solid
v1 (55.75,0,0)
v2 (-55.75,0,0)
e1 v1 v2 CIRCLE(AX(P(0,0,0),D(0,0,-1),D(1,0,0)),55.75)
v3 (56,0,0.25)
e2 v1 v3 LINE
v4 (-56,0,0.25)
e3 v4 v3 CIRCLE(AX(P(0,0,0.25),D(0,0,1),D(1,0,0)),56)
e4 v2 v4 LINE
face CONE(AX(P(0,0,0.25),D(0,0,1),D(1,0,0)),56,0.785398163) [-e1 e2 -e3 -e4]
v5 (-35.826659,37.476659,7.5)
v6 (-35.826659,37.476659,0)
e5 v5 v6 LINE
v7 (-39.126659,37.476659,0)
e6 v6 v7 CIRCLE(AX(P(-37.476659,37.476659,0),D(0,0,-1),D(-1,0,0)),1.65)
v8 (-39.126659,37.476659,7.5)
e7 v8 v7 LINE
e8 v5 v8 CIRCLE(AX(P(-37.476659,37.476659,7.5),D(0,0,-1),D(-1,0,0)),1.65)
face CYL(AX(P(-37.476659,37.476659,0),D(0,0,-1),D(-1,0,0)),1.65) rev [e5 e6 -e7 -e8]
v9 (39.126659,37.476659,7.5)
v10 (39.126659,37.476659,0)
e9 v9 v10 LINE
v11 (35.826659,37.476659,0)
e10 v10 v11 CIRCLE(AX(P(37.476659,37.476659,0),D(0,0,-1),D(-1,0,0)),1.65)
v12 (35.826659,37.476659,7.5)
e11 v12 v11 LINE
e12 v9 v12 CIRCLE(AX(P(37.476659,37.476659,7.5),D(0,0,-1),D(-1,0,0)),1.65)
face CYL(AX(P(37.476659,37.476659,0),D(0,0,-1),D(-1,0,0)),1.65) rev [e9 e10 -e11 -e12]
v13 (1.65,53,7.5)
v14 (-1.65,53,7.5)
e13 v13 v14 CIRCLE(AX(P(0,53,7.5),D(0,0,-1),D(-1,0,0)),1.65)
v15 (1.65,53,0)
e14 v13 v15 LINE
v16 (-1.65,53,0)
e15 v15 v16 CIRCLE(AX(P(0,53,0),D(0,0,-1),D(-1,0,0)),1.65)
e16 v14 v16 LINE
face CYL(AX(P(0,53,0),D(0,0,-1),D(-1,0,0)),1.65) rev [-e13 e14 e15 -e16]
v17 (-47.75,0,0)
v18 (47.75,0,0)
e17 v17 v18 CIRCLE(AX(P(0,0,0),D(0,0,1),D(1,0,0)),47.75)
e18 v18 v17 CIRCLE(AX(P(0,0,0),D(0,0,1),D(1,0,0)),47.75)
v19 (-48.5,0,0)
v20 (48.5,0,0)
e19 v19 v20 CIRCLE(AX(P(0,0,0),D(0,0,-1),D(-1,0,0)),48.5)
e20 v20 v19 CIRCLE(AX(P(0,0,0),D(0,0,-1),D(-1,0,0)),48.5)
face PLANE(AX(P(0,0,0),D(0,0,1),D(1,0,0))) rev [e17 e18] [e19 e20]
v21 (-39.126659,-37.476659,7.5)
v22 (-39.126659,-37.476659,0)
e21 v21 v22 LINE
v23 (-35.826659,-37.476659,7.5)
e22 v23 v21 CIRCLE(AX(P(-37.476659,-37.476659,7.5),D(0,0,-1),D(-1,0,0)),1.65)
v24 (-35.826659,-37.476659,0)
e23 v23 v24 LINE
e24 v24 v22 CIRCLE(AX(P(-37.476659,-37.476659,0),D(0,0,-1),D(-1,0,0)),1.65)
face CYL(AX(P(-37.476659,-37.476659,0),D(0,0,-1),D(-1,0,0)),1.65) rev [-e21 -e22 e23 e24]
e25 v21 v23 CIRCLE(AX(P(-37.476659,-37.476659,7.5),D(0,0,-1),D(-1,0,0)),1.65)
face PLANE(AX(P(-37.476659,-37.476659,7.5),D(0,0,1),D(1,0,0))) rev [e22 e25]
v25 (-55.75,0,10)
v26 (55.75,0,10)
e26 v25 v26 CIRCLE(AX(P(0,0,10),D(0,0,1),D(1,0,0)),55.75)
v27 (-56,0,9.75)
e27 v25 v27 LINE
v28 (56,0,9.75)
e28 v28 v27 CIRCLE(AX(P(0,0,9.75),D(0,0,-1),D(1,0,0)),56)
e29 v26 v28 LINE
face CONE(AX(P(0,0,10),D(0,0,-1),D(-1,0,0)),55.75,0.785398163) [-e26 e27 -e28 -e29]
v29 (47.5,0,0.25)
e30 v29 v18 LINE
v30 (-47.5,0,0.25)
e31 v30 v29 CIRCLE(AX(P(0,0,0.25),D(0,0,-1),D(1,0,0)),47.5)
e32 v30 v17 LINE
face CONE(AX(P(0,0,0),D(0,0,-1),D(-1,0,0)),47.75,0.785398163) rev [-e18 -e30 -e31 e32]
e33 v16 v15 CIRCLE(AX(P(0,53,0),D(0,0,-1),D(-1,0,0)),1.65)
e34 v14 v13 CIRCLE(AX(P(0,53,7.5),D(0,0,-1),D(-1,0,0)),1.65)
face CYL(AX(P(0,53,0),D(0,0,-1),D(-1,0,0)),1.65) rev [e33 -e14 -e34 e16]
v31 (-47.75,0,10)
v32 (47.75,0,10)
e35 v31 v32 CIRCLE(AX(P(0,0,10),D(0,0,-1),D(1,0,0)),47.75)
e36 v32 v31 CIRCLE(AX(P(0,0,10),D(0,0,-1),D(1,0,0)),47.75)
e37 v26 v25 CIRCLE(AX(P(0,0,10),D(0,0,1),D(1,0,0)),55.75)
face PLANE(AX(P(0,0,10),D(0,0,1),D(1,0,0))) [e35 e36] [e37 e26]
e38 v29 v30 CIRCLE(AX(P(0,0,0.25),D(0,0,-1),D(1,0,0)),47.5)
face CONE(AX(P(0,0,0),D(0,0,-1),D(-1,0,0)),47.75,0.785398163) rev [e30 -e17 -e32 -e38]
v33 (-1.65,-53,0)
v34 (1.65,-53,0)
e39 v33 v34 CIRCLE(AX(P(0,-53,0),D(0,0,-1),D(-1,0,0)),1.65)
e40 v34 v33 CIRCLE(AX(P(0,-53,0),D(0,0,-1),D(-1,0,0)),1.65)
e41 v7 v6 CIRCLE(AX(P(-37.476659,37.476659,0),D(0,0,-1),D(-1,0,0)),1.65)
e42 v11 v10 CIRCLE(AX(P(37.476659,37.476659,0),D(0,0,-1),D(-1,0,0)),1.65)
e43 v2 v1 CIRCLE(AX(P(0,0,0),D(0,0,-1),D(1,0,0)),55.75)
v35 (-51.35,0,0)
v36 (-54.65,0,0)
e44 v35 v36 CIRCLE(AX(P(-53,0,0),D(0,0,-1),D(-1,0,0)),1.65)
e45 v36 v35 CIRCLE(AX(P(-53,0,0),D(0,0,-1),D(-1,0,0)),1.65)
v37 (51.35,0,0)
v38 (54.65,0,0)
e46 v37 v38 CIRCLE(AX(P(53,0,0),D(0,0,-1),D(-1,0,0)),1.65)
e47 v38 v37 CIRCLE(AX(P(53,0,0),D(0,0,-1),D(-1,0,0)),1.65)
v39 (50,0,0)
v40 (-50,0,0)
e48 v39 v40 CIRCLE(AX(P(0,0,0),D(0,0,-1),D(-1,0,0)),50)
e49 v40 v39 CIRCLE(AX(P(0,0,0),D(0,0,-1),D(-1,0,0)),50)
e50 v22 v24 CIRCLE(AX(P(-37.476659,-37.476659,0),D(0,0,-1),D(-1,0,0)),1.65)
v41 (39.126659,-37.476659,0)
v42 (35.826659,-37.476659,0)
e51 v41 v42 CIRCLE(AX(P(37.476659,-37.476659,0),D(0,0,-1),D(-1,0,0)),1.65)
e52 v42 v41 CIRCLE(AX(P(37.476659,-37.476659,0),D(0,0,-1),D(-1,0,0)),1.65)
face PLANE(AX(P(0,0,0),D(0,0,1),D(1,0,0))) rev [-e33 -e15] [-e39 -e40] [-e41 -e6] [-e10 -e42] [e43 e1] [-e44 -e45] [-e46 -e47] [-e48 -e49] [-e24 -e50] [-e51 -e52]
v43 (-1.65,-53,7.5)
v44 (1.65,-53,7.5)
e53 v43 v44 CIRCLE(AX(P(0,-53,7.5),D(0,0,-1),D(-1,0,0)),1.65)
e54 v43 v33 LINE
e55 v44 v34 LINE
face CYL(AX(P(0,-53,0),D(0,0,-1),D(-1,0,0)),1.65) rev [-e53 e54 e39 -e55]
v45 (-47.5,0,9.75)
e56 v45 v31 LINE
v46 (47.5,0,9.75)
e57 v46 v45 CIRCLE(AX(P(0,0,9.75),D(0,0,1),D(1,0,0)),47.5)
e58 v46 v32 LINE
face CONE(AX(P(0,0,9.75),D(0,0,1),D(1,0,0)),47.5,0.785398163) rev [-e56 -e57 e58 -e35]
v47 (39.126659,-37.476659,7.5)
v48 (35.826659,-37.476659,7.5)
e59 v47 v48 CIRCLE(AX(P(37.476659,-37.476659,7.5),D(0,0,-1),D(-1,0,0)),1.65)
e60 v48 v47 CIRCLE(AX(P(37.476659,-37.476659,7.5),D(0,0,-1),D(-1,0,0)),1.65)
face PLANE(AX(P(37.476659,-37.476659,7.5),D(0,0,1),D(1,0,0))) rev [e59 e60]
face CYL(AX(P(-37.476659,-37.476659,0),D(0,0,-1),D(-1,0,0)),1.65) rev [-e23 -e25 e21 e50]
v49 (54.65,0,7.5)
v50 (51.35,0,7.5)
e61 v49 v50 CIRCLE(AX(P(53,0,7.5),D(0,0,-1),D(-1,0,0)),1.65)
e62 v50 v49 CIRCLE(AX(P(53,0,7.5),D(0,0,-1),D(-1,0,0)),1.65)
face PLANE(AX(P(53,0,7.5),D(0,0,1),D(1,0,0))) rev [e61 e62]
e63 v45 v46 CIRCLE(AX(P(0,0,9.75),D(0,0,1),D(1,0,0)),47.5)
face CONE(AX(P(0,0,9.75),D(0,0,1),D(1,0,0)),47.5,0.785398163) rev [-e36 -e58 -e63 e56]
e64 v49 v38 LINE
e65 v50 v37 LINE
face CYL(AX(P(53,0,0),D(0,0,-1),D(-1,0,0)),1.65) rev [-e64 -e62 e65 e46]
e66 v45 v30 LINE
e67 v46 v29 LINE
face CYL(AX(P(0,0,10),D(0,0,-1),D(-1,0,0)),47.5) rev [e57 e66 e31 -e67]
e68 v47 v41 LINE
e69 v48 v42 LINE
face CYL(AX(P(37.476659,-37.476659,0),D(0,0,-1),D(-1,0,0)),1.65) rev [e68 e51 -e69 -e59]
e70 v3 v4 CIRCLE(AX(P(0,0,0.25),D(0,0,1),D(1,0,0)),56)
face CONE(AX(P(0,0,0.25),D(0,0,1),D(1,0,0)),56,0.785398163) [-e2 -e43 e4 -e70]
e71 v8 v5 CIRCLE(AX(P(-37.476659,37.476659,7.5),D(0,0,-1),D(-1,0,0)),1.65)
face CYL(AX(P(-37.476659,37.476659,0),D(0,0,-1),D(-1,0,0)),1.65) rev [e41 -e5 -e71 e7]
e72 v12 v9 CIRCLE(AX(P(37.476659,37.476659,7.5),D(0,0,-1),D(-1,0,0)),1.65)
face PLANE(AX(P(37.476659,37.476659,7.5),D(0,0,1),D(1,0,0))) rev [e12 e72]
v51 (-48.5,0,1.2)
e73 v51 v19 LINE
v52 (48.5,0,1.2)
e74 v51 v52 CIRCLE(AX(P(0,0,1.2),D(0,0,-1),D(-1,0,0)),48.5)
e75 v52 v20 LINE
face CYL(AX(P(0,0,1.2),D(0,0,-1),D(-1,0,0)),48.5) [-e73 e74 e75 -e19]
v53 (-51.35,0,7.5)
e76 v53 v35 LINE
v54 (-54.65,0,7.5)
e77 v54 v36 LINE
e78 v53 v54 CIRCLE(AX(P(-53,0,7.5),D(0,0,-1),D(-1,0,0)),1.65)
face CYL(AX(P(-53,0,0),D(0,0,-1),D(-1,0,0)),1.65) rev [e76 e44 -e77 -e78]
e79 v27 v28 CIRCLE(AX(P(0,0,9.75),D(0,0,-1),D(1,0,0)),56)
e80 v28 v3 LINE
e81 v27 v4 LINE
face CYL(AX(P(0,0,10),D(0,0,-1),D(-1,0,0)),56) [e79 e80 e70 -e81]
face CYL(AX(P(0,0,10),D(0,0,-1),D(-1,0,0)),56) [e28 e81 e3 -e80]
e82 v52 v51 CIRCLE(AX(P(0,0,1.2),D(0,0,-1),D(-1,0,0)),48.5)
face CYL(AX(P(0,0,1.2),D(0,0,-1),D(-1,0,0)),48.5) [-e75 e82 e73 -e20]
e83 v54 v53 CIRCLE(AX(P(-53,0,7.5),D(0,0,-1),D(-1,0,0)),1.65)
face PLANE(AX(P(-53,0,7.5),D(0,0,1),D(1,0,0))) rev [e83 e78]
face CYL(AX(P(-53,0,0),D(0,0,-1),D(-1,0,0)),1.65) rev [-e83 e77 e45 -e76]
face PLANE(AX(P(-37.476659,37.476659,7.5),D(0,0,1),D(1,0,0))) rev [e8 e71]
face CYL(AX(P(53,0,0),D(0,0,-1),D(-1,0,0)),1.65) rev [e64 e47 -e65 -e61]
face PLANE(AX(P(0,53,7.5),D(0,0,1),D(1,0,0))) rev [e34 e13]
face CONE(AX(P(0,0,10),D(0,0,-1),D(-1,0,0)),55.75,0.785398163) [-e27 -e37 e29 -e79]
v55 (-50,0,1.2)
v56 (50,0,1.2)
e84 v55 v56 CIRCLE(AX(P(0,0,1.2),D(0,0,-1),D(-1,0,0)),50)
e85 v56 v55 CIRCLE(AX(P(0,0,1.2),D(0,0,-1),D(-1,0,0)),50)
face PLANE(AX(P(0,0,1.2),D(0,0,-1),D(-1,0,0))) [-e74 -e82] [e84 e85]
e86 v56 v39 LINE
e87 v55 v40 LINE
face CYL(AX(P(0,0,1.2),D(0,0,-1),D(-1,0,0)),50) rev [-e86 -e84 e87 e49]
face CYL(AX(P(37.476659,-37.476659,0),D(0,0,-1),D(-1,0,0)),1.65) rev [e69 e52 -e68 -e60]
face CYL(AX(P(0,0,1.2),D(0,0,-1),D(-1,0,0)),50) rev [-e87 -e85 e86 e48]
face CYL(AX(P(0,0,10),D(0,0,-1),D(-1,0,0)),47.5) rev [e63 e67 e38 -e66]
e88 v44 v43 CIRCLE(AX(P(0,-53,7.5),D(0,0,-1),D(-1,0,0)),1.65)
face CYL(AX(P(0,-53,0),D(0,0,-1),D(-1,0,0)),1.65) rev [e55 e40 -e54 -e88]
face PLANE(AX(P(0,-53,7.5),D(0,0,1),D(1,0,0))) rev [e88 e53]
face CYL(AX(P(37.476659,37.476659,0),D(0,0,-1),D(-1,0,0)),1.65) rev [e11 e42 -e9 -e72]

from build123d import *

# Parameters (mm, degrees)
SKETCH_1_R             = 56
SKETCH_1_R_2           = 47.5
EXTRUDE_1_DEPTH        = 10
HOLE_WIZARD_M4_1_D     = 3.3
HOLE_WIZARD_M4_1_DEPTH = 7.5
CHAMFER_1_SIZE         = 0.25
SKETCH_5_R             = 50
SKETCH_5_R_2           = 48.5
CUT_EXTRUDE_1_DEPTH    = 1.2


with BuildPart() as part:
    # 草图1 → 凸台-拉伸1 (new body)
    with BuildSketch(Plane.XY):
        Circle(SKETCH_1_R)
        Circle(SKETCH_1_R_2, mode=Mode.SUBTRACT)
    extrude(amount=EXTRUDE_1_DEPTH)

    # M4 螺纹孔1
    with Locations(Plane(origin=(0, 0, 0), x_dir=(-1, 0, 0), z_dir=(0, 0, -1))):
        with Locations((35.5, 0), (0, 35.5), (0, -35.5), (-35.5, 0), (-37.476659403, -37.476659403), (37.476659403, -37.476659403), (37.476659403, 37.476659403), (-37.476659403, 37.476659403), (0, 53), (53, 0), (0, -53), (-53, 0)):
            Hole(HOLE_WIZARD_M4_1_D / 2, depth=HOLE_WIZARD_M4_1_DEPTH)

    # 倒角1
    chamfer_1_edges = [part.edges().sort_by_distance(p)[0] for p in [
        (-56, 0, 0),
        (-56, 0, 10),
        (-47.5, 0, 0),
        (-47.5, 0, 10),
    ]]
    chamfer(chamfer_1_edges, length=CHAMFER_1_SIZE)

    # 草图5 → 切除-拉伸1 (cut)
    with BuildSketch(Plane(origin=(0, 0, 0), x_dir=(-1, 0, 0), z_dir=(0, 0, -1))):
        Circle(SKETCH_5_R)
        Circle(SKETCH_5_R_2, mode=Mode.SUBTRACT)
    extrude(amount=-CUT_EXTRUDE_1_DEPTH, mode=Mode.SUBTRACT)


solid = part.part
